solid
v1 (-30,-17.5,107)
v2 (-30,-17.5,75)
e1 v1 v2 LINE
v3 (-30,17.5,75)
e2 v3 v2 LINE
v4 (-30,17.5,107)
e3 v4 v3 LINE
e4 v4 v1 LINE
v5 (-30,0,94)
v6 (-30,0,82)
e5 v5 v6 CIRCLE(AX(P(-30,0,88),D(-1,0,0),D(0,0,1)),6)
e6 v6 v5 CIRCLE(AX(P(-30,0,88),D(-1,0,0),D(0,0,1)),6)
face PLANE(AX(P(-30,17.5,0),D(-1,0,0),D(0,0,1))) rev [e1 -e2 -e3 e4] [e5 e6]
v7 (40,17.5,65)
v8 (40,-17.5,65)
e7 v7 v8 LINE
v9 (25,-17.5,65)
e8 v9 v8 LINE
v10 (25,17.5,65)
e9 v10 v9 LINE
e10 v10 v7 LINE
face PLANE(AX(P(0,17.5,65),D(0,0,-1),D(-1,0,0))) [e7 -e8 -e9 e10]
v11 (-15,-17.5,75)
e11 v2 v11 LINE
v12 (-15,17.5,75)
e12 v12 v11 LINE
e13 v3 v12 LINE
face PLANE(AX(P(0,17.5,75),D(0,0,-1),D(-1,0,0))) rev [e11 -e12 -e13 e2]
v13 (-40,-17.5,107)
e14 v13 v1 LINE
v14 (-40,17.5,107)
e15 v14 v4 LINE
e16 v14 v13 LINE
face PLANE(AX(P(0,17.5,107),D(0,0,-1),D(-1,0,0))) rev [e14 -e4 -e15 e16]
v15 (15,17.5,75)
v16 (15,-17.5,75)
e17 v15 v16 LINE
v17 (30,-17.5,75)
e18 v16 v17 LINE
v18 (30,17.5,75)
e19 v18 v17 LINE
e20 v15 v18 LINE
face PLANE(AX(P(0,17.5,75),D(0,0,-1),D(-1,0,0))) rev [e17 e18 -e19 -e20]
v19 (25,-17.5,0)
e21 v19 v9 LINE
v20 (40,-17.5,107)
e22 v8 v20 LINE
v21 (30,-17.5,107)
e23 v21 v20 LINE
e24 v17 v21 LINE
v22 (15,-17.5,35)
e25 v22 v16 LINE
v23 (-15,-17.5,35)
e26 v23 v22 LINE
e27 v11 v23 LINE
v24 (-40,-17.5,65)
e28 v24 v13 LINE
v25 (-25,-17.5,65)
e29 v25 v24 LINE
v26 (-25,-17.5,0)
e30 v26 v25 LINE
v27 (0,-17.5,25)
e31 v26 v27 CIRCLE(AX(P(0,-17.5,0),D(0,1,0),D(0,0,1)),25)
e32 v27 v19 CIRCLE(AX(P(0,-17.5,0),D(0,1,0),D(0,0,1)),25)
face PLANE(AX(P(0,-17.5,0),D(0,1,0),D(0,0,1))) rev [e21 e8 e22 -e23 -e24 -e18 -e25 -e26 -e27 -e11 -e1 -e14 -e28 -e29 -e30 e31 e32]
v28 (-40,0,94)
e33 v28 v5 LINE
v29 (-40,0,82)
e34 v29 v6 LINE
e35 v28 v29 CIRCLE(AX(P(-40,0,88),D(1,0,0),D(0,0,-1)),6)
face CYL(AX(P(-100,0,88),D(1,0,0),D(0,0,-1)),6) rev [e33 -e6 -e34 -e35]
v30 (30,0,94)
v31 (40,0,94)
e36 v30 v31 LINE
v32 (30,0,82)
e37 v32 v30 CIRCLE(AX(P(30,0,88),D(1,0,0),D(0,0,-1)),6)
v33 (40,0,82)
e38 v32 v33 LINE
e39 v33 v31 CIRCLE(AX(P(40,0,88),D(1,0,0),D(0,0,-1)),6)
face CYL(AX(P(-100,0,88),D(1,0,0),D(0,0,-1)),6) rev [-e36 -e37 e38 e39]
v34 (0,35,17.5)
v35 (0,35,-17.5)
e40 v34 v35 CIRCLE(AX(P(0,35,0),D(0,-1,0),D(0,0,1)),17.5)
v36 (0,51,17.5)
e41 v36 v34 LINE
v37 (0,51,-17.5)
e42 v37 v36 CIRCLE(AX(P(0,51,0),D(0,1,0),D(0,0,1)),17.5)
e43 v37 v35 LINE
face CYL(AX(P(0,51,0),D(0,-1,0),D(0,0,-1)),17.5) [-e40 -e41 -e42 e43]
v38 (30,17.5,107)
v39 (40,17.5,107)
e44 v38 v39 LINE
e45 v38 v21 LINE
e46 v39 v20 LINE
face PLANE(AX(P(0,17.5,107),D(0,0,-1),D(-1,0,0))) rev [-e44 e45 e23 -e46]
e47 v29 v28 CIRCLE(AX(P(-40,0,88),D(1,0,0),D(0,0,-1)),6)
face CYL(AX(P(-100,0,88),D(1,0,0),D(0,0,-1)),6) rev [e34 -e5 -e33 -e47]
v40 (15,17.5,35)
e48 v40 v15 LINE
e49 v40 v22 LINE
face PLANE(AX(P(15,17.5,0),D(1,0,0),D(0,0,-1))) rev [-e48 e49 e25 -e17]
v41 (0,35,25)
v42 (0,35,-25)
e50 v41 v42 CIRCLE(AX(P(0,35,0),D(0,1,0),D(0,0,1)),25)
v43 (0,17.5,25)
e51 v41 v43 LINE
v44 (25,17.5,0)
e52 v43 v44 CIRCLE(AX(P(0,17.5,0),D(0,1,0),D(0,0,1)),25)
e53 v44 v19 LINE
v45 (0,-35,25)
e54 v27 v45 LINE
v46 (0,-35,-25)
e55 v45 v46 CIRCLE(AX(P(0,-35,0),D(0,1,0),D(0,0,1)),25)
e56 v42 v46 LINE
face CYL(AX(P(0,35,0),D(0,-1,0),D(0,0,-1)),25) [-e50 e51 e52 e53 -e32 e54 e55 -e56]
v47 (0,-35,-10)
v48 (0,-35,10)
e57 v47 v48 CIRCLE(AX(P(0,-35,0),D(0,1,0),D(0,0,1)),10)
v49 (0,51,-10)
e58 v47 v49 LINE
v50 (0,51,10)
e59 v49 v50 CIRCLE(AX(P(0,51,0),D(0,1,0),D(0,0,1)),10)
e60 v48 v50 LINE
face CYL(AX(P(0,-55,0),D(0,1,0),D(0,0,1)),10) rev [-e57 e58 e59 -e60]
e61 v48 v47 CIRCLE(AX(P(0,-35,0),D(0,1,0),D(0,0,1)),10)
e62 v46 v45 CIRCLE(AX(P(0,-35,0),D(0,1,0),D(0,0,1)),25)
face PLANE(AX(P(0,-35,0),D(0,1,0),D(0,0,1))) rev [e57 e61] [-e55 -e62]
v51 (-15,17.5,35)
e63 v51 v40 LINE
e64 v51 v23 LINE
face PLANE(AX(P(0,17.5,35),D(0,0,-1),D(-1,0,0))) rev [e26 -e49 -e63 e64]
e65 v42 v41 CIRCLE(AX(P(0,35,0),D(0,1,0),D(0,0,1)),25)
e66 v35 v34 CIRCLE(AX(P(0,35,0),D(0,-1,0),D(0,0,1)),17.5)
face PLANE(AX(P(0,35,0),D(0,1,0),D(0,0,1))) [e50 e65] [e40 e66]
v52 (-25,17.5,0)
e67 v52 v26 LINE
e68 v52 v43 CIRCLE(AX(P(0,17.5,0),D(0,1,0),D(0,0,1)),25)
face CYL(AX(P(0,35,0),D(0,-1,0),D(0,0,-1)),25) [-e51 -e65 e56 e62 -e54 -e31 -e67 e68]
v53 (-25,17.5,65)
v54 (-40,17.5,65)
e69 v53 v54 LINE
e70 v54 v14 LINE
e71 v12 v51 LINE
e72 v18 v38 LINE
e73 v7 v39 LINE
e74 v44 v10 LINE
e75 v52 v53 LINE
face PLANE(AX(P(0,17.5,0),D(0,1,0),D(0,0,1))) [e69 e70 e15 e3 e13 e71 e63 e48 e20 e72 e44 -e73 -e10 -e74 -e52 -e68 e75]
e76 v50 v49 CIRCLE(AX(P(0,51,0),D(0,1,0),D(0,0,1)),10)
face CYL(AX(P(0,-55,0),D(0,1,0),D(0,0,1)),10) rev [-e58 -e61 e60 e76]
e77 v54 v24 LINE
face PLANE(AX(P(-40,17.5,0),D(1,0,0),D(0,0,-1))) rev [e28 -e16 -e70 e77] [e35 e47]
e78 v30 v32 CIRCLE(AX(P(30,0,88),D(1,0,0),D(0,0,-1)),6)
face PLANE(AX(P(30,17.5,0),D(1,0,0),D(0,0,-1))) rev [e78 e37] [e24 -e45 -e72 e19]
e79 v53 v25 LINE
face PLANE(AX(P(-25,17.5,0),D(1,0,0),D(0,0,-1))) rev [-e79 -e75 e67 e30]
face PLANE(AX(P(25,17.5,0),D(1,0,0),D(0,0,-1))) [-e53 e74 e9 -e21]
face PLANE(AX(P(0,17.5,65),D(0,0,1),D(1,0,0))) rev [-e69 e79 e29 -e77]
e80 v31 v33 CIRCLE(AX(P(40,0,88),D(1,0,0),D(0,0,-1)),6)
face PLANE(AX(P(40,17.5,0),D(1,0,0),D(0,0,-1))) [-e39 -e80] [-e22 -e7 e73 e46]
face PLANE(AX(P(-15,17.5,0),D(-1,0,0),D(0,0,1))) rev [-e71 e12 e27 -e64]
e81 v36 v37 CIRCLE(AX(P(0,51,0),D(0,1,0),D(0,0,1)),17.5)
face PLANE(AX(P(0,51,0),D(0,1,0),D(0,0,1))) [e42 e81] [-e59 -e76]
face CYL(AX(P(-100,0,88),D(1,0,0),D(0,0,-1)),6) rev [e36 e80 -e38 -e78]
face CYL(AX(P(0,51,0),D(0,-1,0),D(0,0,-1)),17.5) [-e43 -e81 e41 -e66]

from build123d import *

# Parameters (mm, degrees)
FORK_PROFILE_SKETCH_R   = 25
FORK_BASE_BODY_DEPTH    = 35
SKETCH2_3_R             = 17.5
HUB_BOSS_DEPTH          = 51
HUB_BORE_DEPTH          = 55
FORK_ARMS_DEPTH         = 17.5
PIN_HOLE_SKETCH_R       = 6
CROSS_PIN_HOLE_12_DEPTH = 140


with BuildPart() as part:
    # Fork Profile Sketch → Fork Base Body (new, symmetric)
    with BuildSketch(Plane(origin=(0, 0, 0), x_dir=(1, 0, 0), z_dir=(0, 1, 0))):
        with Locations(Location((0, 0, 0), (0, 0, 270))):
            Circle(FORK_PROFILE_SKETCH_R)
    extrude(amount=FORK_BASE_BODY_DEPTH, both=True)

    # Sketch2_3 → Hub Boss (add)
    with BuildSketch(Plane(origin=(0, 0, 0), x_dir=(1, 0, 0), z_dir=(0, 1, 0))):
        with Locations(Location((0, 0, 0), (0, 0, 270))):
            Circle(SKETCH2_3_R)
    extrude(amount=HUB_BOSS_DEPTH)

    # Sketch2_4 → Hub Bore (cut, symmetric)
    with BuildSketch(Plane(origin=(0, 0, 0), x_dir=(1, 0, 0), z_dir=(0, 1, 0))):
        with BuildLine():
            Line((9.946400687, -1.033979392), (0, -1.717163069))
            Line((0, -1.717163069), (-9.946400687, -1.033979392))
            ThreePointArc((-9.946400687, -1.033979392), (0, -10), (9.946400687, -1.033979392))
        make_face()
        with BuildLine():
            Line((-9.946400687, -1.033979392), (0, -1.717163069))
            Line((0, -1.717163069), (9.946400687, -1.033979392))
            ThreePointArc((9.946400687, -1.033979392), (9.986591182, -0.517683849), (10, 0))
            ThreePointArc((10, 0), (-0.517683849, 9.986591182), (-9.946400687, -1.033979392))
        make_face()
        with BuildLine():
            Line((9.946400687, -1.033979392), (0, -1.717163069))
            Line((0, -1.717163069), (-9.946400687, -1.033979392))
            ThreePointArc((-9.946400687, -1.033979392), (0, -10), (9.946400687, -1.033979392))
        make_face()
        with BuildLine():
            Line((-9.946400687, -1.033979392), (0, -1.717163069))
            Line((0, -1.717163069), (9.946400687, -1.033979392))
            ThreePointArc((9.946400687, -1.033979392), (9.986591182, -0.517683849), (10, 0))
            ThreePointArc((10, 0), (-0.517683849, 9.986591182), (-9.946400687, -1.033979392))
        make_face()
    extrude(amount=HUB_BORE_DEPTH, both=True, mode=Mode.SUBTRACT)

    # Sketch2_5 → Fork Arms (add, symmetric)
    with BuildSketch(Plane(origin=(0, 0, 0), x_dir=(1, 0, 0), z_dir=(0, 1, 0))):
        with BuildLine():
            ThreePointArc((25, 0), (0, -25), (-25, 0))
            Line((-25, 0), (-25, -65))
            Line((-25, -65), (-40, -65))
            Line((-40, -65), (-40, -107))
            Line((-40, -107), (-30, -107))
            Line((-30, -107), (-30, -75))
            Line((-30, -75), (-15, -75))
            Line((-15, -75), (-15, -35))
            Line((-15, -35), (15, -35))
            Line((15, -35), (15, -52.523875455))
            Line((15, -52.523875455), (15, -75))
            Line((15, -75), (30, -75))
            Line((30, -75), (30, -107))
            Line((30, -107), (40, -107))
            Line((40, -107), (40, -65))
            Line((40, -65), (25, -65))
            Line((25, -65), (25, 0))
        make_face()
    extrude(amount=FORK_ARMS_DEPTH, both=True)

    # Pin Hole Sketch → Cross Pin Hole _12 (cut)
    with BuildSketch(Plane(origin=(40, 0, 0), x_dir=(0, 0, -1), z_dir=(1, 0, 0))):
        with Locations((-88, 0)):
            Circle(PIN_HOLE_SKETCH_R)
    extrude(amount=-CROSS_PIN_HOLE_12_DEPTH, mode=Mode.SUBTRACT)


solid = part.part
